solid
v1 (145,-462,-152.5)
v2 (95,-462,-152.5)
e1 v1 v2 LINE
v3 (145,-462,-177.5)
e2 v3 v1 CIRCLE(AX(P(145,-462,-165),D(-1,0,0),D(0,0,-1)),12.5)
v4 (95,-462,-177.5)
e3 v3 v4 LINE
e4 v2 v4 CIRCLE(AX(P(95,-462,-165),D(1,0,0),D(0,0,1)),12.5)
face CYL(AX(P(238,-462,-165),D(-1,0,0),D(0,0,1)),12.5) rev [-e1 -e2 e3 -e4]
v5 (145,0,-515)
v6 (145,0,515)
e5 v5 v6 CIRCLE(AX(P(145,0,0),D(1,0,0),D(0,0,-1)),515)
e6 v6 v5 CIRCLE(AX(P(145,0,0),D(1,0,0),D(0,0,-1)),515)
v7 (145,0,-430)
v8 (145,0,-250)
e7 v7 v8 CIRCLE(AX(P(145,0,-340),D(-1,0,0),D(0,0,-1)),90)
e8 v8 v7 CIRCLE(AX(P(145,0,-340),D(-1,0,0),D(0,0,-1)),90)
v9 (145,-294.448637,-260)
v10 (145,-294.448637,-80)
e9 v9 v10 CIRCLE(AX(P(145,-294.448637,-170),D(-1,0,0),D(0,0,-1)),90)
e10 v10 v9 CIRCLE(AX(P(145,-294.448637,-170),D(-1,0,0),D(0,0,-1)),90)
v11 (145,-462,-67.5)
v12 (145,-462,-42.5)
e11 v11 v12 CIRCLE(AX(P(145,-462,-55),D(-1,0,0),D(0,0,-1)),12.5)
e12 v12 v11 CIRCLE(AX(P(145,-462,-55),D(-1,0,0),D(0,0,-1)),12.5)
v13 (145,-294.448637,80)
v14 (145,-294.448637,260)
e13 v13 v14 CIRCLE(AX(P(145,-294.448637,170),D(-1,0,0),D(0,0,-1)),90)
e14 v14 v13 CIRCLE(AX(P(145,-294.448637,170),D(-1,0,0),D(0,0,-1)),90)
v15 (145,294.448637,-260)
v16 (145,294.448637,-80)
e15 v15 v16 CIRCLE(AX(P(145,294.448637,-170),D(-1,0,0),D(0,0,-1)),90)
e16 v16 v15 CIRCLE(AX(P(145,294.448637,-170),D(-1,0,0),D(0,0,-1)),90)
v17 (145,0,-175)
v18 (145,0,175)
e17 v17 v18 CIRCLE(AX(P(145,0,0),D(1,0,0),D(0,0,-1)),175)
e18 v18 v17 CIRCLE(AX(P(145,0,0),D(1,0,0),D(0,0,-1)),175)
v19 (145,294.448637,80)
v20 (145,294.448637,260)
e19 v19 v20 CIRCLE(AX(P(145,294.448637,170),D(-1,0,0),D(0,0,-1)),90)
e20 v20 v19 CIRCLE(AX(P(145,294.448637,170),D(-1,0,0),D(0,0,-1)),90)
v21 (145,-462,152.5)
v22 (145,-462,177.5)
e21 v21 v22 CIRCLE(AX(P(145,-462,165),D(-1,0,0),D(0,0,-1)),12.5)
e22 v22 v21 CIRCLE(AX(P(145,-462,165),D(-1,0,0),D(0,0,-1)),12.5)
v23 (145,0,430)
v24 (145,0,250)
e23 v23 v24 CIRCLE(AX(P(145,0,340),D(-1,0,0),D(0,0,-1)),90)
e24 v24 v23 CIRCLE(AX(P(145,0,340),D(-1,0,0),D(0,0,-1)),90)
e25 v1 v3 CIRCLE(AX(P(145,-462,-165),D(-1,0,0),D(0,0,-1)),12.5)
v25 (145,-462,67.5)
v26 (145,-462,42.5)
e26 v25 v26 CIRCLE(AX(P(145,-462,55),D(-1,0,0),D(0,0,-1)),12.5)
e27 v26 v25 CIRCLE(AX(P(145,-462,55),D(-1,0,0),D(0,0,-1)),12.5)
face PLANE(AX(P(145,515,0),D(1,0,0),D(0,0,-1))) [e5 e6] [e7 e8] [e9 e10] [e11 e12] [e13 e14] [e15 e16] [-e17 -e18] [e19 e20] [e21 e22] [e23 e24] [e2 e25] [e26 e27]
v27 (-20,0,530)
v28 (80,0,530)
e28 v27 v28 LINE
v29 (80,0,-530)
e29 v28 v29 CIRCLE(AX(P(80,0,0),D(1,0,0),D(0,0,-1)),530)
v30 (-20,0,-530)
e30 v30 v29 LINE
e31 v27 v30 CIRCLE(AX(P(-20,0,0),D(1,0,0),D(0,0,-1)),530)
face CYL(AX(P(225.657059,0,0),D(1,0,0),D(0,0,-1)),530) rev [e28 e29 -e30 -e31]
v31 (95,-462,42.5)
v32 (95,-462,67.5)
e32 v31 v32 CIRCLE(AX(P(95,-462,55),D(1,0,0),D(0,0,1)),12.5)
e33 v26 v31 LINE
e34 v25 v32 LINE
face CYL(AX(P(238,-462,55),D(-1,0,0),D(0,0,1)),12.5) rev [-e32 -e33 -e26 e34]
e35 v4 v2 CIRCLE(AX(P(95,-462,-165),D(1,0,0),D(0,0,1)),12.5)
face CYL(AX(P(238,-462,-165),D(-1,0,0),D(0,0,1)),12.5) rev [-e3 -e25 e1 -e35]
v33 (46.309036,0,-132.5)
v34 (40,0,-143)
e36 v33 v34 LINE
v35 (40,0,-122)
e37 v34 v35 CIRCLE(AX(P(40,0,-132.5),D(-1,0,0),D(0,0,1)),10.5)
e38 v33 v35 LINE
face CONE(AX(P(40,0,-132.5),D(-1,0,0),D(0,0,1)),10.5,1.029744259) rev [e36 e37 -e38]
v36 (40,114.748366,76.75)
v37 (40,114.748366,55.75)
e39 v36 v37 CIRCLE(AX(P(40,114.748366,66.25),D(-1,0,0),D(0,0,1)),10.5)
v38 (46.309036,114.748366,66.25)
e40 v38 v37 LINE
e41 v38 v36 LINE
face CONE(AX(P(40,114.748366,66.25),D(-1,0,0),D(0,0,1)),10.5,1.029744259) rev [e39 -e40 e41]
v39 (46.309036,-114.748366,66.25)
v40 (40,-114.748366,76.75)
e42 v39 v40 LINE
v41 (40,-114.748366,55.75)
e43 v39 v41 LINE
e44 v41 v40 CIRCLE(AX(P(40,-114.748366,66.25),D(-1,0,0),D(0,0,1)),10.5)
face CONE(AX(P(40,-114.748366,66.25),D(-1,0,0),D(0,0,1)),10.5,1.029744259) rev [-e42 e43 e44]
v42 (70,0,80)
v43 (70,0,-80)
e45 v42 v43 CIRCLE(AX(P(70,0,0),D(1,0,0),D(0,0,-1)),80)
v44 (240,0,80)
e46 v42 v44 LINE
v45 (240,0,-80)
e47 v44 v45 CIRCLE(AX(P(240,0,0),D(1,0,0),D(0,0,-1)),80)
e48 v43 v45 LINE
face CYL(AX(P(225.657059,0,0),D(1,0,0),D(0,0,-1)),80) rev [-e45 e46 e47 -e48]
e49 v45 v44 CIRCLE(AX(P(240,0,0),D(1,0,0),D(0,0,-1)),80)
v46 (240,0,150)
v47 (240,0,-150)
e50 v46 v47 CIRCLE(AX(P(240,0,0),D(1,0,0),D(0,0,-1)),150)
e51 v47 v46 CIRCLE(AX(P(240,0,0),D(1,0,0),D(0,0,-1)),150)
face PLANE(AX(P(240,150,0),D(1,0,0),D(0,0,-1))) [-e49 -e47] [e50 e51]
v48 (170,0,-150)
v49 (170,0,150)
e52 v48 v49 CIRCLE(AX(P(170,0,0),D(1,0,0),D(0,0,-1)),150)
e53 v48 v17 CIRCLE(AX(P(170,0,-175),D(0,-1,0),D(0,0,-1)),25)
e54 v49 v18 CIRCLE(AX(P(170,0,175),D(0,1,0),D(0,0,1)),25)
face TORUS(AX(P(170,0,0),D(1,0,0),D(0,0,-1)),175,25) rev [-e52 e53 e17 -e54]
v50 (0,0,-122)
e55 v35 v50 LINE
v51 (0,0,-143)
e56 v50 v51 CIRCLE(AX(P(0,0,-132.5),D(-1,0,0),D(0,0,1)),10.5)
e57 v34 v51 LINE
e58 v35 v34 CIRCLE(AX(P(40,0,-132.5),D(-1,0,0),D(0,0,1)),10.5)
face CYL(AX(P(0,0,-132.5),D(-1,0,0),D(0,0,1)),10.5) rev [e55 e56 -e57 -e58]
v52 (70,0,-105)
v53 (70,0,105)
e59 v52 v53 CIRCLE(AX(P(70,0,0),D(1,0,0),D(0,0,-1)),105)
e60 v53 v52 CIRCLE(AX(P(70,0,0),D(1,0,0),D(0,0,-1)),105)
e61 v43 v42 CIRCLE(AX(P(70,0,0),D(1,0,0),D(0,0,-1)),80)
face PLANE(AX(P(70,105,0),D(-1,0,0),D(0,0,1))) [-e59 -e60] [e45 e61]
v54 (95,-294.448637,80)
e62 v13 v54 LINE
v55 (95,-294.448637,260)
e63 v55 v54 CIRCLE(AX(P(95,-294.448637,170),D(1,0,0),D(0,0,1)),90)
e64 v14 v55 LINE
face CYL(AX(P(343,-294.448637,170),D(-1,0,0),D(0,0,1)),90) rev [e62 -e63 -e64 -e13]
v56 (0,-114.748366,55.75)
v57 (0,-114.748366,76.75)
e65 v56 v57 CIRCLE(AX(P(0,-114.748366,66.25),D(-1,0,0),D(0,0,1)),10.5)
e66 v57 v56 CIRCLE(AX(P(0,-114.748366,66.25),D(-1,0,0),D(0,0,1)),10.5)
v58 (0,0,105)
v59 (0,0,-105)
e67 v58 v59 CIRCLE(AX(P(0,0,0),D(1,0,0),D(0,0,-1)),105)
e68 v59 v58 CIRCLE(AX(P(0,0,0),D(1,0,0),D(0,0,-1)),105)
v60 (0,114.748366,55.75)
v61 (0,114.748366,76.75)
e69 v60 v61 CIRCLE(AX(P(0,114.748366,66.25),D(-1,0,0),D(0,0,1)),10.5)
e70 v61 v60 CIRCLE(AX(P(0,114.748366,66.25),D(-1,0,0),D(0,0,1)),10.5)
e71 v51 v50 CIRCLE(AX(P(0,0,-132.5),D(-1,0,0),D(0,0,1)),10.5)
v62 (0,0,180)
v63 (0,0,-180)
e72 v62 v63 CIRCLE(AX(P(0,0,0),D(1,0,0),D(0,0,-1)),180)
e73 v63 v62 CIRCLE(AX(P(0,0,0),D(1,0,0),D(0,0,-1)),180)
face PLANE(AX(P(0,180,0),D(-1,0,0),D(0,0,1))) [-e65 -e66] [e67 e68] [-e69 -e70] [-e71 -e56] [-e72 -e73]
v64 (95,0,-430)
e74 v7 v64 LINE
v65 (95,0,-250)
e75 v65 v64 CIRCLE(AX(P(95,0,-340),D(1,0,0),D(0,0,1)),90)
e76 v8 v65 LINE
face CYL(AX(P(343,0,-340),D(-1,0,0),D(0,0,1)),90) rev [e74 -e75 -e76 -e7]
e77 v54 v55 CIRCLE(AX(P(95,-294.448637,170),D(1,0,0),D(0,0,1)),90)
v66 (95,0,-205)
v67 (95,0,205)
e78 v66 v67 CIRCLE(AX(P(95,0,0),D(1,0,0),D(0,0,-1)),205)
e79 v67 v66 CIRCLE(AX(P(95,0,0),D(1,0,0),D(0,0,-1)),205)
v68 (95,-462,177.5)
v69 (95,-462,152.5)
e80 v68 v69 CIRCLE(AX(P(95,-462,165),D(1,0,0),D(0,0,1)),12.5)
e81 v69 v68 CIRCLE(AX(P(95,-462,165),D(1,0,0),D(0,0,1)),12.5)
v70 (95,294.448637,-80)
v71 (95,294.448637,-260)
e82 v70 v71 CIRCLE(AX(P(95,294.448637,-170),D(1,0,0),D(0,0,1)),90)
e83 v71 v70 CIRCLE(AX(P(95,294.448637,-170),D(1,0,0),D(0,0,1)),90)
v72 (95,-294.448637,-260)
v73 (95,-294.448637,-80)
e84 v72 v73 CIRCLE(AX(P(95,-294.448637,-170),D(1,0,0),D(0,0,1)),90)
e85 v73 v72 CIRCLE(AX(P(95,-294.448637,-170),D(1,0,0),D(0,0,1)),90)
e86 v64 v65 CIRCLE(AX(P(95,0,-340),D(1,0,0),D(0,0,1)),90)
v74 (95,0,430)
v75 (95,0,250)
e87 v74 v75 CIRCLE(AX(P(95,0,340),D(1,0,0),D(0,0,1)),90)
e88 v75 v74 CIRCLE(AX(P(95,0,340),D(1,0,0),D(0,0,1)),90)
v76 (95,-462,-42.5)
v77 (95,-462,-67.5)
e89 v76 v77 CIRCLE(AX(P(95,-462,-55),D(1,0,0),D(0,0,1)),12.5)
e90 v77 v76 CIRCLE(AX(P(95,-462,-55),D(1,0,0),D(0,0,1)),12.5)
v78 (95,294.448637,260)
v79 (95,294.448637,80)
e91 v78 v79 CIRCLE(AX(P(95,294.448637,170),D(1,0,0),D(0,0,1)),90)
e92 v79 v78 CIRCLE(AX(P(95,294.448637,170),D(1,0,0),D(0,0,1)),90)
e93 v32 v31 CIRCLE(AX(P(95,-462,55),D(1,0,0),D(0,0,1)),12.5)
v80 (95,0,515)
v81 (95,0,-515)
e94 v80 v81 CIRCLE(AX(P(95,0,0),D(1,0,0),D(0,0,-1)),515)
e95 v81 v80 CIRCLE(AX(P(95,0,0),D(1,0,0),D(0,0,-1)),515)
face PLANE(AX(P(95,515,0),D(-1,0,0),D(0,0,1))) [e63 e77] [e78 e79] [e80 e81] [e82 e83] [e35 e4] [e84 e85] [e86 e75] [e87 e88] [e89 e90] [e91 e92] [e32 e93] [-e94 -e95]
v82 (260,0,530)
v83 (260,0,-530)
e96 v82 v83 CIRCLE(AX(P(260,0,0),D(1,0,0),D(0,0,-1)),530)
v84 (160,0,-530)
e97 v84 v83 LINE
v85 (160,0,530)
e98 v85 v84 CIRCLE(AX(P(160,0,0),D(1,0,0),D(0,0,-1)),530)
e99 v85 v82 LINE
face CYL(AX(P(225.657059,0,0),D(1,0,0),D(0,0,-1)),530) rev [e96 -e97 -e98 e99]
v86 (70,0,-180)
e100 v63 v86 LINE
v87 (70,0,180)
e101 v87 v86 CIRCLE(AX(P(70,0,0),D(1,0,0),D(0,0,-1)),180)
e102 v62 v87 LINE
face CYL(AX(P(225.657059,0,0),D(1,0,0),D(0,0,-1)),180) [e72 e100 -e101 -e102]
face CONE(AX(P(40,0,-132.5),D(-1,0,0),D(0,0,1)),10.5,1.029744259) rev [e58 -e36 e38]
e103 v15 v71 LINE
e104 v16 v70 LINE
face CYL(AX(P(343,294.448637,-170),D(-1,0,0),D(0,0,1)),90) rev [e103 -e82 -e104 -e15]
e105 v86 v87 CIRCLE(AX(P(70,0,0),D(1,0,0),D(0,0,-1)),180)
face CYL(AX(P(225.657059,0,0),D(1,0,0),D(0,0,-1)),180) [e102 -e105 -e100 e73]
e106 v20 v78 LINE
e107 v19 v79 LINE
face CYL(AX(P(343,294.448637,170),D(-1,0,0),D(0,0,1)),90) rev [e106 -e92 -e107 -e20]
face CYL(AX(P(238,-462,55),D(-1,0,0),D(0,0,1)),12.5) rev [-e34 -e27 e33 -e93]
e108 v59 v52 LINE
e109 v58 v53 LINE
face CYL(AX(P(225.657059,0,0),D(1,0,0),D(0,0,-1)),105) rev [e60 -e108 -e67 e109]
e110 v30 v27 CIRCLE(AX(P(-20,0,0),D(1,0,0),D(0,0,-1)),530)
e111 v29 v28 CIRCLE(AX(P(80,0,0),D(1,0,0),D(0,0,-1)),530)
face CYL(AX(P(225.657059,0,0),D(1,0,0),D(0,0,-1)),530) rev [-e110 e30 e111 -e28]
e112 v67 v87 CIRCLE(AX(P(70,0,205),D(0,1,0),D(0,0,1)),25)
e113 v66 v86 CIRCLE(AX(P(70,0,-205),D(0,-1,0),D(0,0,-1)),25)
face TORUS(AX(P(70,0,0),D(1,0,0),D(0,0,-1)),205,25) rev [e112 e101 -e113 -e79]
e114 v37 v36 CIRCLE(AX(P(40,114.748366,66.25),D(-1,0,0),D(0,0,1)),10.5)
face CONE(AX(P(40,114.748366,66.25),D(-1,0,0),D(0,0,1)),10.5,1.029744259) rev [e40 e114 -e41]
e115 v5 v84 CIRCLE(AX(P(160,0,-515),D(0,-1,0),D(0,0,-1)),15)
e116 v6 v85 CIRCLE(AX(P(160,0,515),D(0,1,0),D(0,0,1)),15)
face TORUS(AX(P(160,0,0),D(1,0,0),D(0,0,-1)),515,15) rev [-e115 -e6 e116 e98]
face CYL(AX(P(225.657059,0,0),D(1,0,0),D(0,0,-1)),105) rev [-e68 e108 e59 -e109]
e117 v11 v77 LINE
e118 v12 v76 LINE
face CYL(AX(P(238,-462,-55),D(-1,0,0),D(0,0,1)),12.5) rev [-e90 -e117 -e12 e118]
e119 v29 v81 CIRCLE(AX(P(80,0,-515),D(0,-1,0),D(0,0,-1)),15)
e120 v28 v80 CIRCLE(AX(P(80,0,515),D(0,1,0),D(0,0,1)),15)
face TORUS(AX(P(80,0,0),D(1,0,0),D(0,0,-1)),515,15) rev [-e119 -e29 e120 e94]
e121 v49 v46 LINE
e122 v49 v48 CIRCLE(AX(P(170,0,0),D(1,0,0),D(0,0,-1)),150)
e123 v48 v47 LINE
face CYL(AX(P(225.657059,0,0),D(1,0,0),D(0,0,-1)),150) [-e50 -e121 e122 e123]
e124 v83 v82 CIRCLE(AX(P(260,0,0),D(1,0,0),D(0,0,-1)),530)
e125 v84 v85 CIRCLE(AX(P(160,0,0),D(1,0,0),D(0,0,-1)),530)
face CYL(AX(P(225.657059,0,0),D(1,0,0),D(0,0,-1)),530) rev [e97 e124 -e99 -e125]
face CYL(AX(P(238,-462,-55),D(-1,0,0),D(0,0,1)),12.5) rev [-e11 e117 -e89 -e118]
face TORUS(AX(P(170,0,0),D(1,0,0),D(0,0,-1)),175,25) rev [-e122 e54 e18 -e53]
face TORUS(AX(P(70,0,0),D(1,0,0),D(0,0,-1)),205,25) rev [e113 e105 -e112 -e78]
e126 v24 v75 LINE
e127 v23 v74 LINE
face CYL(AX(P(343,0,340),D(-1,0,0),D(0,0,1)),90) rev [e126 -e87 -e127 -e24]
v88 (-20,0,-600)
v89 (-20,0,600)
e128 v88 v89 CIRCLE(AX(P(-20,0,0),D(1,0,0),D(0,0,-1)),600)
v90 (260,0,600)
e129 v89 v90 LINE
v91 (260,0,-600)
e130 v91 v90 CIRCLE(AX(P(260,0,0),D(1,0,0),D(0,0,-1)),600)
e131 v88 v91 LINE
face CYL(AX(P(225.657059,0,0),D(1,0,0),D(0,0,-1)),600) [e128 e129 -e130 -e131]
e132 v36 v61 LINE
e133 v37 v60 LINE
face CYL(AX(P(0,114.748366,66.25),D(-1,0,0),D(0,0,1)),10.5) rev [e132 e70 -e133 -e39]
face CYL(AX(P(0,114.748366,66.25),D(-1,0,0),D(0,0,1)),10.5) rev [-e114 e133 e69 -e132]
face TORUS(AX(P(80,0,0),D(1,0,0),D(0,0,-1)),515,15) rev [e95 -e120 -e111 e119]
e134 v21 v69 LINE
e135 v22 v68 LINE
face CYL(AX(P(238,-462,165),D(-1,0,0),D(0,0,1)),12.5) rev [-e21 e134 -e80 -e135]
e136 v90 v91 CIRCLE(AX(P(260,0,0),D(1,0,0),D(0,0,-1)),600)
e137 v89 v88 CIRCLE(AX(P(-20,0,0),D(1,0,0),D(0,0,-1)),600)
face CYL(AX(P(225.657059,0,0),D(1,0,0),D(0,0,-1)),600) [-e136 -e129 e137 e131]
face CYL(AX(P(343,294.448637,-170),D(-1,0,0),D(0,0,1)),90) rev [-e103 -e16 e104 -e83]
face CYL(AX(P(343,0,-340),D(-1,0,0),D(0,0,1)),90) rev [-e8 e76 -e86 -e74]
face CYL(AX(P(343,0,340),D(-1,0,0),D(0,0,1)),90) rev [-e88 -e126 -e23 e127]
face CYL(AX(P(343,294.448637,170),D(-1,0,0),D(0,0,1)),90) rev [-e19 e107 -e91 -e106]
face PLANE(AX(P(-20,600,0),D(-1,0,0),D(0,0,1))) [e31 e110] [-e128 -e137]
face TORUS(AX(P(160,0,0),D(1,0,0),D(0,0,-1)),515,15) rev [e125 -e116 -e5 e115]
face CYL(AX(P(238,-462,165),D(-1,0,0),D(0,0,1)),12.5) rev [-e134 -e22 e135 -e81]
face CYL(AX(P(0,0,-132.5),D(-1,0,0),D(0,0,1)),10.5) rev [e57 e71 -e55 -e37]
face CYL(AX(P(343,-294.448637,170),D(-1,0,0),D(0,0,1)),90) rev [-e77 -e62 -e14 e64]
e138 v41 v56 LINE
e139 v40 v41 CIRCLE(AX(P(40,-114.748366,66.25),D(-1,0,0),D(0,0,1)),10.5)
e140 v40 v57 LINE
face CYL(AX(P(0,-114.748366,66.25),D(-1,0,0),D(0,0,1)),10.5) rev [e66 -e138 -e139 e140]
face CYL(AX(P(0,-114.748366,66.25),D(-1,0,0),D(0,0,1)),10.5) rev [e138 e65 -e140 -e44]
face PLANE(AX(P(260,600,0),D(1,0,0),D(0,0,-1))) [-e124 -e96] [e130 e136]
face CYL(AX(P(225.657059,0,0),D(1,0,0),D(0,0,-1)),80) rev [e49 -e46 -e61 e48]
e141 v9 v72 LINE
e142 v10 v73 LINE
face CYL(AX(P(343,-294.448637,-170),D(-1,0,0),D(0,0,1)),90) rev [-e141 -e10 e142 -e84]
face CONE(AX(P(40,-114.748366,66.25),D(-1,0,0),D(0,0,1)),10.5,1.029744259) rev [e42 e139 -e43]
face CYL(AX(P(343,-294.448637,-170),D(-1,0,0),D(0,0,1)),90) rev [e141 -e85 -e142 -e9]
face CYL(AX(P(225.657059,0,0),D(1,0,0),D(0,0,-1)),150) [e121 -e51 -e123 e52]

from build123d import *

# Parameters (mm, degrees)
SKETCH4_R          = 90
CUT_EXTRUDE1_DEPTH = 343
CIRPATTERN1_COUNT  = 6
CIRPATTERN2_COUNT  = 3
SKETCH8_R          = 12.5
CUT_EXTRUDE3_DEPTH = 238


with BuildPart() as part:
    # Sketch2 → Revolve1 (revolve)
    with BuildSketch(Plane.XY, mode=Mode.PRIVATE) as revolve1_sk:
        with BuildLine():
            Line((-20, 600), (-20, 530))
            Line((-20, 530), (80, 530))
            ThreePointArc((80, 530), (90.606601718, 525.606601718), (95, 515))
            Line((95, 515), (95, 205))
            ThreePointArc((95, 205), (87.67766953, 187.32233047), (70, 180))
            Line((70, 180), (0, 180))
            Line((0, 180), (0, 105))
            Line((0, 105), (70, 105))
            Line((70, 105), (70, 80))
            Line((70, 80), (240, 80))
            Line((240, 80), (240, 150))
            Line((240, 150), (170, 150))
            ThreePointArc((170, 150), (152.32233047, 157.32233047), (145, 175))
            Line((145, 175), (145, 515))
            ThreePointArc((145, 515), (149.393398282, 525.606601718), (160, 530))
            Line((160, 530), (260, 530))
            Line((260, 530), (260, 600))
            Line((260, 600), (-20, 600))
        make_face()
    revolve(revolve1_sk.sketch.rotate(Axis((225.657059372, 0, 0), (-1, 0, 0)), 90), axis=Axis((225.657059372, 0, 0), (-1, 0, 0)))

    # Sketch4 → Cut-Extrude1 (cut)
    with BuildSketch(Plane(origin=(0, 0, 0), x_dir=(0, 0, -1), z_dir=(1, 0, 0))):
        with Locations(Location((-170, 294.448637287, 0), (0, 0, 180))):
            Circle(SKETCH4_R)
    cut_extrude1 = extrude(amount=CUT_EXTRUDE1_DEPTH, mode=Mode.SUBTRACT)

    # CirPattern1: Cut-Extrude1 ×6 about axis
    cirpattern1_axis = Axis((0, 0, 0), (1, 0, 0))
    for i in range(1, CIRPATTERN1_COUNT):
        add(cut_extrude1.rotate(cirpattern1_axis, i * 360 / CIRPATTERN1_COUNT), mode=Mode.SUBTRACT)

    # Sketch6 → M24 Tapped Hole1 (revolve, cut)
    with BuildSketch(Plane(origin=(0, 114.748366001, 66.25), x_dir=(0, 0, 1), z_dir=(0, 1, 0))):
        Polygon((0, 0), (0, 46.3090365), (10.5, 40), (10.5, 0), align=None)
    m24_tapped_hole1 = revolve(axis=Axis((-6.35, 114.748366001, 66.25), (1, 0, 0)), mode=Mode.SUBTRACT)

    # CirPattern2: M24 Tapped Hole1 ×3 about axis
    cirpattern2_axis = Axis((0, 0, 0), (1, 0, 0))
    for i in range(1, CIRPATTERN2_COUNT):
        add(m24_tapped_hole1.rotate(cirpattern2_axis, i * 360 / CIRPATTERN2_COUNT), mode=Mode.SUBTRACT)

    # Sketch8 → Cut-Extrude3 (cut)
    with BuildSketch(Plane(origin=(0, 0, 0), x_dir=(0, 0, -1), z_dir=(1, 0, 0))):
        with Locations(Location((-55, -462, 0), (0, 0, 180))):
            Circle(SKETCH8_R)
        with Locations(Location((-165, -462, 0), (0, 0, 180))):
            Circle(SKETCH8_R)
        with Locations(Location((55, -462, 0), (0, 0, 180))):
            Circle(SKETCH8_R)
        with Locations(Location((165, -462, 0), (0, 0, 180))):
            Circle(SKETCH8_R)
    extrude(amount=CUT_EXTRUDE3_DEPTH, mode=Mode.SUBTRACT)


solid = part.part
